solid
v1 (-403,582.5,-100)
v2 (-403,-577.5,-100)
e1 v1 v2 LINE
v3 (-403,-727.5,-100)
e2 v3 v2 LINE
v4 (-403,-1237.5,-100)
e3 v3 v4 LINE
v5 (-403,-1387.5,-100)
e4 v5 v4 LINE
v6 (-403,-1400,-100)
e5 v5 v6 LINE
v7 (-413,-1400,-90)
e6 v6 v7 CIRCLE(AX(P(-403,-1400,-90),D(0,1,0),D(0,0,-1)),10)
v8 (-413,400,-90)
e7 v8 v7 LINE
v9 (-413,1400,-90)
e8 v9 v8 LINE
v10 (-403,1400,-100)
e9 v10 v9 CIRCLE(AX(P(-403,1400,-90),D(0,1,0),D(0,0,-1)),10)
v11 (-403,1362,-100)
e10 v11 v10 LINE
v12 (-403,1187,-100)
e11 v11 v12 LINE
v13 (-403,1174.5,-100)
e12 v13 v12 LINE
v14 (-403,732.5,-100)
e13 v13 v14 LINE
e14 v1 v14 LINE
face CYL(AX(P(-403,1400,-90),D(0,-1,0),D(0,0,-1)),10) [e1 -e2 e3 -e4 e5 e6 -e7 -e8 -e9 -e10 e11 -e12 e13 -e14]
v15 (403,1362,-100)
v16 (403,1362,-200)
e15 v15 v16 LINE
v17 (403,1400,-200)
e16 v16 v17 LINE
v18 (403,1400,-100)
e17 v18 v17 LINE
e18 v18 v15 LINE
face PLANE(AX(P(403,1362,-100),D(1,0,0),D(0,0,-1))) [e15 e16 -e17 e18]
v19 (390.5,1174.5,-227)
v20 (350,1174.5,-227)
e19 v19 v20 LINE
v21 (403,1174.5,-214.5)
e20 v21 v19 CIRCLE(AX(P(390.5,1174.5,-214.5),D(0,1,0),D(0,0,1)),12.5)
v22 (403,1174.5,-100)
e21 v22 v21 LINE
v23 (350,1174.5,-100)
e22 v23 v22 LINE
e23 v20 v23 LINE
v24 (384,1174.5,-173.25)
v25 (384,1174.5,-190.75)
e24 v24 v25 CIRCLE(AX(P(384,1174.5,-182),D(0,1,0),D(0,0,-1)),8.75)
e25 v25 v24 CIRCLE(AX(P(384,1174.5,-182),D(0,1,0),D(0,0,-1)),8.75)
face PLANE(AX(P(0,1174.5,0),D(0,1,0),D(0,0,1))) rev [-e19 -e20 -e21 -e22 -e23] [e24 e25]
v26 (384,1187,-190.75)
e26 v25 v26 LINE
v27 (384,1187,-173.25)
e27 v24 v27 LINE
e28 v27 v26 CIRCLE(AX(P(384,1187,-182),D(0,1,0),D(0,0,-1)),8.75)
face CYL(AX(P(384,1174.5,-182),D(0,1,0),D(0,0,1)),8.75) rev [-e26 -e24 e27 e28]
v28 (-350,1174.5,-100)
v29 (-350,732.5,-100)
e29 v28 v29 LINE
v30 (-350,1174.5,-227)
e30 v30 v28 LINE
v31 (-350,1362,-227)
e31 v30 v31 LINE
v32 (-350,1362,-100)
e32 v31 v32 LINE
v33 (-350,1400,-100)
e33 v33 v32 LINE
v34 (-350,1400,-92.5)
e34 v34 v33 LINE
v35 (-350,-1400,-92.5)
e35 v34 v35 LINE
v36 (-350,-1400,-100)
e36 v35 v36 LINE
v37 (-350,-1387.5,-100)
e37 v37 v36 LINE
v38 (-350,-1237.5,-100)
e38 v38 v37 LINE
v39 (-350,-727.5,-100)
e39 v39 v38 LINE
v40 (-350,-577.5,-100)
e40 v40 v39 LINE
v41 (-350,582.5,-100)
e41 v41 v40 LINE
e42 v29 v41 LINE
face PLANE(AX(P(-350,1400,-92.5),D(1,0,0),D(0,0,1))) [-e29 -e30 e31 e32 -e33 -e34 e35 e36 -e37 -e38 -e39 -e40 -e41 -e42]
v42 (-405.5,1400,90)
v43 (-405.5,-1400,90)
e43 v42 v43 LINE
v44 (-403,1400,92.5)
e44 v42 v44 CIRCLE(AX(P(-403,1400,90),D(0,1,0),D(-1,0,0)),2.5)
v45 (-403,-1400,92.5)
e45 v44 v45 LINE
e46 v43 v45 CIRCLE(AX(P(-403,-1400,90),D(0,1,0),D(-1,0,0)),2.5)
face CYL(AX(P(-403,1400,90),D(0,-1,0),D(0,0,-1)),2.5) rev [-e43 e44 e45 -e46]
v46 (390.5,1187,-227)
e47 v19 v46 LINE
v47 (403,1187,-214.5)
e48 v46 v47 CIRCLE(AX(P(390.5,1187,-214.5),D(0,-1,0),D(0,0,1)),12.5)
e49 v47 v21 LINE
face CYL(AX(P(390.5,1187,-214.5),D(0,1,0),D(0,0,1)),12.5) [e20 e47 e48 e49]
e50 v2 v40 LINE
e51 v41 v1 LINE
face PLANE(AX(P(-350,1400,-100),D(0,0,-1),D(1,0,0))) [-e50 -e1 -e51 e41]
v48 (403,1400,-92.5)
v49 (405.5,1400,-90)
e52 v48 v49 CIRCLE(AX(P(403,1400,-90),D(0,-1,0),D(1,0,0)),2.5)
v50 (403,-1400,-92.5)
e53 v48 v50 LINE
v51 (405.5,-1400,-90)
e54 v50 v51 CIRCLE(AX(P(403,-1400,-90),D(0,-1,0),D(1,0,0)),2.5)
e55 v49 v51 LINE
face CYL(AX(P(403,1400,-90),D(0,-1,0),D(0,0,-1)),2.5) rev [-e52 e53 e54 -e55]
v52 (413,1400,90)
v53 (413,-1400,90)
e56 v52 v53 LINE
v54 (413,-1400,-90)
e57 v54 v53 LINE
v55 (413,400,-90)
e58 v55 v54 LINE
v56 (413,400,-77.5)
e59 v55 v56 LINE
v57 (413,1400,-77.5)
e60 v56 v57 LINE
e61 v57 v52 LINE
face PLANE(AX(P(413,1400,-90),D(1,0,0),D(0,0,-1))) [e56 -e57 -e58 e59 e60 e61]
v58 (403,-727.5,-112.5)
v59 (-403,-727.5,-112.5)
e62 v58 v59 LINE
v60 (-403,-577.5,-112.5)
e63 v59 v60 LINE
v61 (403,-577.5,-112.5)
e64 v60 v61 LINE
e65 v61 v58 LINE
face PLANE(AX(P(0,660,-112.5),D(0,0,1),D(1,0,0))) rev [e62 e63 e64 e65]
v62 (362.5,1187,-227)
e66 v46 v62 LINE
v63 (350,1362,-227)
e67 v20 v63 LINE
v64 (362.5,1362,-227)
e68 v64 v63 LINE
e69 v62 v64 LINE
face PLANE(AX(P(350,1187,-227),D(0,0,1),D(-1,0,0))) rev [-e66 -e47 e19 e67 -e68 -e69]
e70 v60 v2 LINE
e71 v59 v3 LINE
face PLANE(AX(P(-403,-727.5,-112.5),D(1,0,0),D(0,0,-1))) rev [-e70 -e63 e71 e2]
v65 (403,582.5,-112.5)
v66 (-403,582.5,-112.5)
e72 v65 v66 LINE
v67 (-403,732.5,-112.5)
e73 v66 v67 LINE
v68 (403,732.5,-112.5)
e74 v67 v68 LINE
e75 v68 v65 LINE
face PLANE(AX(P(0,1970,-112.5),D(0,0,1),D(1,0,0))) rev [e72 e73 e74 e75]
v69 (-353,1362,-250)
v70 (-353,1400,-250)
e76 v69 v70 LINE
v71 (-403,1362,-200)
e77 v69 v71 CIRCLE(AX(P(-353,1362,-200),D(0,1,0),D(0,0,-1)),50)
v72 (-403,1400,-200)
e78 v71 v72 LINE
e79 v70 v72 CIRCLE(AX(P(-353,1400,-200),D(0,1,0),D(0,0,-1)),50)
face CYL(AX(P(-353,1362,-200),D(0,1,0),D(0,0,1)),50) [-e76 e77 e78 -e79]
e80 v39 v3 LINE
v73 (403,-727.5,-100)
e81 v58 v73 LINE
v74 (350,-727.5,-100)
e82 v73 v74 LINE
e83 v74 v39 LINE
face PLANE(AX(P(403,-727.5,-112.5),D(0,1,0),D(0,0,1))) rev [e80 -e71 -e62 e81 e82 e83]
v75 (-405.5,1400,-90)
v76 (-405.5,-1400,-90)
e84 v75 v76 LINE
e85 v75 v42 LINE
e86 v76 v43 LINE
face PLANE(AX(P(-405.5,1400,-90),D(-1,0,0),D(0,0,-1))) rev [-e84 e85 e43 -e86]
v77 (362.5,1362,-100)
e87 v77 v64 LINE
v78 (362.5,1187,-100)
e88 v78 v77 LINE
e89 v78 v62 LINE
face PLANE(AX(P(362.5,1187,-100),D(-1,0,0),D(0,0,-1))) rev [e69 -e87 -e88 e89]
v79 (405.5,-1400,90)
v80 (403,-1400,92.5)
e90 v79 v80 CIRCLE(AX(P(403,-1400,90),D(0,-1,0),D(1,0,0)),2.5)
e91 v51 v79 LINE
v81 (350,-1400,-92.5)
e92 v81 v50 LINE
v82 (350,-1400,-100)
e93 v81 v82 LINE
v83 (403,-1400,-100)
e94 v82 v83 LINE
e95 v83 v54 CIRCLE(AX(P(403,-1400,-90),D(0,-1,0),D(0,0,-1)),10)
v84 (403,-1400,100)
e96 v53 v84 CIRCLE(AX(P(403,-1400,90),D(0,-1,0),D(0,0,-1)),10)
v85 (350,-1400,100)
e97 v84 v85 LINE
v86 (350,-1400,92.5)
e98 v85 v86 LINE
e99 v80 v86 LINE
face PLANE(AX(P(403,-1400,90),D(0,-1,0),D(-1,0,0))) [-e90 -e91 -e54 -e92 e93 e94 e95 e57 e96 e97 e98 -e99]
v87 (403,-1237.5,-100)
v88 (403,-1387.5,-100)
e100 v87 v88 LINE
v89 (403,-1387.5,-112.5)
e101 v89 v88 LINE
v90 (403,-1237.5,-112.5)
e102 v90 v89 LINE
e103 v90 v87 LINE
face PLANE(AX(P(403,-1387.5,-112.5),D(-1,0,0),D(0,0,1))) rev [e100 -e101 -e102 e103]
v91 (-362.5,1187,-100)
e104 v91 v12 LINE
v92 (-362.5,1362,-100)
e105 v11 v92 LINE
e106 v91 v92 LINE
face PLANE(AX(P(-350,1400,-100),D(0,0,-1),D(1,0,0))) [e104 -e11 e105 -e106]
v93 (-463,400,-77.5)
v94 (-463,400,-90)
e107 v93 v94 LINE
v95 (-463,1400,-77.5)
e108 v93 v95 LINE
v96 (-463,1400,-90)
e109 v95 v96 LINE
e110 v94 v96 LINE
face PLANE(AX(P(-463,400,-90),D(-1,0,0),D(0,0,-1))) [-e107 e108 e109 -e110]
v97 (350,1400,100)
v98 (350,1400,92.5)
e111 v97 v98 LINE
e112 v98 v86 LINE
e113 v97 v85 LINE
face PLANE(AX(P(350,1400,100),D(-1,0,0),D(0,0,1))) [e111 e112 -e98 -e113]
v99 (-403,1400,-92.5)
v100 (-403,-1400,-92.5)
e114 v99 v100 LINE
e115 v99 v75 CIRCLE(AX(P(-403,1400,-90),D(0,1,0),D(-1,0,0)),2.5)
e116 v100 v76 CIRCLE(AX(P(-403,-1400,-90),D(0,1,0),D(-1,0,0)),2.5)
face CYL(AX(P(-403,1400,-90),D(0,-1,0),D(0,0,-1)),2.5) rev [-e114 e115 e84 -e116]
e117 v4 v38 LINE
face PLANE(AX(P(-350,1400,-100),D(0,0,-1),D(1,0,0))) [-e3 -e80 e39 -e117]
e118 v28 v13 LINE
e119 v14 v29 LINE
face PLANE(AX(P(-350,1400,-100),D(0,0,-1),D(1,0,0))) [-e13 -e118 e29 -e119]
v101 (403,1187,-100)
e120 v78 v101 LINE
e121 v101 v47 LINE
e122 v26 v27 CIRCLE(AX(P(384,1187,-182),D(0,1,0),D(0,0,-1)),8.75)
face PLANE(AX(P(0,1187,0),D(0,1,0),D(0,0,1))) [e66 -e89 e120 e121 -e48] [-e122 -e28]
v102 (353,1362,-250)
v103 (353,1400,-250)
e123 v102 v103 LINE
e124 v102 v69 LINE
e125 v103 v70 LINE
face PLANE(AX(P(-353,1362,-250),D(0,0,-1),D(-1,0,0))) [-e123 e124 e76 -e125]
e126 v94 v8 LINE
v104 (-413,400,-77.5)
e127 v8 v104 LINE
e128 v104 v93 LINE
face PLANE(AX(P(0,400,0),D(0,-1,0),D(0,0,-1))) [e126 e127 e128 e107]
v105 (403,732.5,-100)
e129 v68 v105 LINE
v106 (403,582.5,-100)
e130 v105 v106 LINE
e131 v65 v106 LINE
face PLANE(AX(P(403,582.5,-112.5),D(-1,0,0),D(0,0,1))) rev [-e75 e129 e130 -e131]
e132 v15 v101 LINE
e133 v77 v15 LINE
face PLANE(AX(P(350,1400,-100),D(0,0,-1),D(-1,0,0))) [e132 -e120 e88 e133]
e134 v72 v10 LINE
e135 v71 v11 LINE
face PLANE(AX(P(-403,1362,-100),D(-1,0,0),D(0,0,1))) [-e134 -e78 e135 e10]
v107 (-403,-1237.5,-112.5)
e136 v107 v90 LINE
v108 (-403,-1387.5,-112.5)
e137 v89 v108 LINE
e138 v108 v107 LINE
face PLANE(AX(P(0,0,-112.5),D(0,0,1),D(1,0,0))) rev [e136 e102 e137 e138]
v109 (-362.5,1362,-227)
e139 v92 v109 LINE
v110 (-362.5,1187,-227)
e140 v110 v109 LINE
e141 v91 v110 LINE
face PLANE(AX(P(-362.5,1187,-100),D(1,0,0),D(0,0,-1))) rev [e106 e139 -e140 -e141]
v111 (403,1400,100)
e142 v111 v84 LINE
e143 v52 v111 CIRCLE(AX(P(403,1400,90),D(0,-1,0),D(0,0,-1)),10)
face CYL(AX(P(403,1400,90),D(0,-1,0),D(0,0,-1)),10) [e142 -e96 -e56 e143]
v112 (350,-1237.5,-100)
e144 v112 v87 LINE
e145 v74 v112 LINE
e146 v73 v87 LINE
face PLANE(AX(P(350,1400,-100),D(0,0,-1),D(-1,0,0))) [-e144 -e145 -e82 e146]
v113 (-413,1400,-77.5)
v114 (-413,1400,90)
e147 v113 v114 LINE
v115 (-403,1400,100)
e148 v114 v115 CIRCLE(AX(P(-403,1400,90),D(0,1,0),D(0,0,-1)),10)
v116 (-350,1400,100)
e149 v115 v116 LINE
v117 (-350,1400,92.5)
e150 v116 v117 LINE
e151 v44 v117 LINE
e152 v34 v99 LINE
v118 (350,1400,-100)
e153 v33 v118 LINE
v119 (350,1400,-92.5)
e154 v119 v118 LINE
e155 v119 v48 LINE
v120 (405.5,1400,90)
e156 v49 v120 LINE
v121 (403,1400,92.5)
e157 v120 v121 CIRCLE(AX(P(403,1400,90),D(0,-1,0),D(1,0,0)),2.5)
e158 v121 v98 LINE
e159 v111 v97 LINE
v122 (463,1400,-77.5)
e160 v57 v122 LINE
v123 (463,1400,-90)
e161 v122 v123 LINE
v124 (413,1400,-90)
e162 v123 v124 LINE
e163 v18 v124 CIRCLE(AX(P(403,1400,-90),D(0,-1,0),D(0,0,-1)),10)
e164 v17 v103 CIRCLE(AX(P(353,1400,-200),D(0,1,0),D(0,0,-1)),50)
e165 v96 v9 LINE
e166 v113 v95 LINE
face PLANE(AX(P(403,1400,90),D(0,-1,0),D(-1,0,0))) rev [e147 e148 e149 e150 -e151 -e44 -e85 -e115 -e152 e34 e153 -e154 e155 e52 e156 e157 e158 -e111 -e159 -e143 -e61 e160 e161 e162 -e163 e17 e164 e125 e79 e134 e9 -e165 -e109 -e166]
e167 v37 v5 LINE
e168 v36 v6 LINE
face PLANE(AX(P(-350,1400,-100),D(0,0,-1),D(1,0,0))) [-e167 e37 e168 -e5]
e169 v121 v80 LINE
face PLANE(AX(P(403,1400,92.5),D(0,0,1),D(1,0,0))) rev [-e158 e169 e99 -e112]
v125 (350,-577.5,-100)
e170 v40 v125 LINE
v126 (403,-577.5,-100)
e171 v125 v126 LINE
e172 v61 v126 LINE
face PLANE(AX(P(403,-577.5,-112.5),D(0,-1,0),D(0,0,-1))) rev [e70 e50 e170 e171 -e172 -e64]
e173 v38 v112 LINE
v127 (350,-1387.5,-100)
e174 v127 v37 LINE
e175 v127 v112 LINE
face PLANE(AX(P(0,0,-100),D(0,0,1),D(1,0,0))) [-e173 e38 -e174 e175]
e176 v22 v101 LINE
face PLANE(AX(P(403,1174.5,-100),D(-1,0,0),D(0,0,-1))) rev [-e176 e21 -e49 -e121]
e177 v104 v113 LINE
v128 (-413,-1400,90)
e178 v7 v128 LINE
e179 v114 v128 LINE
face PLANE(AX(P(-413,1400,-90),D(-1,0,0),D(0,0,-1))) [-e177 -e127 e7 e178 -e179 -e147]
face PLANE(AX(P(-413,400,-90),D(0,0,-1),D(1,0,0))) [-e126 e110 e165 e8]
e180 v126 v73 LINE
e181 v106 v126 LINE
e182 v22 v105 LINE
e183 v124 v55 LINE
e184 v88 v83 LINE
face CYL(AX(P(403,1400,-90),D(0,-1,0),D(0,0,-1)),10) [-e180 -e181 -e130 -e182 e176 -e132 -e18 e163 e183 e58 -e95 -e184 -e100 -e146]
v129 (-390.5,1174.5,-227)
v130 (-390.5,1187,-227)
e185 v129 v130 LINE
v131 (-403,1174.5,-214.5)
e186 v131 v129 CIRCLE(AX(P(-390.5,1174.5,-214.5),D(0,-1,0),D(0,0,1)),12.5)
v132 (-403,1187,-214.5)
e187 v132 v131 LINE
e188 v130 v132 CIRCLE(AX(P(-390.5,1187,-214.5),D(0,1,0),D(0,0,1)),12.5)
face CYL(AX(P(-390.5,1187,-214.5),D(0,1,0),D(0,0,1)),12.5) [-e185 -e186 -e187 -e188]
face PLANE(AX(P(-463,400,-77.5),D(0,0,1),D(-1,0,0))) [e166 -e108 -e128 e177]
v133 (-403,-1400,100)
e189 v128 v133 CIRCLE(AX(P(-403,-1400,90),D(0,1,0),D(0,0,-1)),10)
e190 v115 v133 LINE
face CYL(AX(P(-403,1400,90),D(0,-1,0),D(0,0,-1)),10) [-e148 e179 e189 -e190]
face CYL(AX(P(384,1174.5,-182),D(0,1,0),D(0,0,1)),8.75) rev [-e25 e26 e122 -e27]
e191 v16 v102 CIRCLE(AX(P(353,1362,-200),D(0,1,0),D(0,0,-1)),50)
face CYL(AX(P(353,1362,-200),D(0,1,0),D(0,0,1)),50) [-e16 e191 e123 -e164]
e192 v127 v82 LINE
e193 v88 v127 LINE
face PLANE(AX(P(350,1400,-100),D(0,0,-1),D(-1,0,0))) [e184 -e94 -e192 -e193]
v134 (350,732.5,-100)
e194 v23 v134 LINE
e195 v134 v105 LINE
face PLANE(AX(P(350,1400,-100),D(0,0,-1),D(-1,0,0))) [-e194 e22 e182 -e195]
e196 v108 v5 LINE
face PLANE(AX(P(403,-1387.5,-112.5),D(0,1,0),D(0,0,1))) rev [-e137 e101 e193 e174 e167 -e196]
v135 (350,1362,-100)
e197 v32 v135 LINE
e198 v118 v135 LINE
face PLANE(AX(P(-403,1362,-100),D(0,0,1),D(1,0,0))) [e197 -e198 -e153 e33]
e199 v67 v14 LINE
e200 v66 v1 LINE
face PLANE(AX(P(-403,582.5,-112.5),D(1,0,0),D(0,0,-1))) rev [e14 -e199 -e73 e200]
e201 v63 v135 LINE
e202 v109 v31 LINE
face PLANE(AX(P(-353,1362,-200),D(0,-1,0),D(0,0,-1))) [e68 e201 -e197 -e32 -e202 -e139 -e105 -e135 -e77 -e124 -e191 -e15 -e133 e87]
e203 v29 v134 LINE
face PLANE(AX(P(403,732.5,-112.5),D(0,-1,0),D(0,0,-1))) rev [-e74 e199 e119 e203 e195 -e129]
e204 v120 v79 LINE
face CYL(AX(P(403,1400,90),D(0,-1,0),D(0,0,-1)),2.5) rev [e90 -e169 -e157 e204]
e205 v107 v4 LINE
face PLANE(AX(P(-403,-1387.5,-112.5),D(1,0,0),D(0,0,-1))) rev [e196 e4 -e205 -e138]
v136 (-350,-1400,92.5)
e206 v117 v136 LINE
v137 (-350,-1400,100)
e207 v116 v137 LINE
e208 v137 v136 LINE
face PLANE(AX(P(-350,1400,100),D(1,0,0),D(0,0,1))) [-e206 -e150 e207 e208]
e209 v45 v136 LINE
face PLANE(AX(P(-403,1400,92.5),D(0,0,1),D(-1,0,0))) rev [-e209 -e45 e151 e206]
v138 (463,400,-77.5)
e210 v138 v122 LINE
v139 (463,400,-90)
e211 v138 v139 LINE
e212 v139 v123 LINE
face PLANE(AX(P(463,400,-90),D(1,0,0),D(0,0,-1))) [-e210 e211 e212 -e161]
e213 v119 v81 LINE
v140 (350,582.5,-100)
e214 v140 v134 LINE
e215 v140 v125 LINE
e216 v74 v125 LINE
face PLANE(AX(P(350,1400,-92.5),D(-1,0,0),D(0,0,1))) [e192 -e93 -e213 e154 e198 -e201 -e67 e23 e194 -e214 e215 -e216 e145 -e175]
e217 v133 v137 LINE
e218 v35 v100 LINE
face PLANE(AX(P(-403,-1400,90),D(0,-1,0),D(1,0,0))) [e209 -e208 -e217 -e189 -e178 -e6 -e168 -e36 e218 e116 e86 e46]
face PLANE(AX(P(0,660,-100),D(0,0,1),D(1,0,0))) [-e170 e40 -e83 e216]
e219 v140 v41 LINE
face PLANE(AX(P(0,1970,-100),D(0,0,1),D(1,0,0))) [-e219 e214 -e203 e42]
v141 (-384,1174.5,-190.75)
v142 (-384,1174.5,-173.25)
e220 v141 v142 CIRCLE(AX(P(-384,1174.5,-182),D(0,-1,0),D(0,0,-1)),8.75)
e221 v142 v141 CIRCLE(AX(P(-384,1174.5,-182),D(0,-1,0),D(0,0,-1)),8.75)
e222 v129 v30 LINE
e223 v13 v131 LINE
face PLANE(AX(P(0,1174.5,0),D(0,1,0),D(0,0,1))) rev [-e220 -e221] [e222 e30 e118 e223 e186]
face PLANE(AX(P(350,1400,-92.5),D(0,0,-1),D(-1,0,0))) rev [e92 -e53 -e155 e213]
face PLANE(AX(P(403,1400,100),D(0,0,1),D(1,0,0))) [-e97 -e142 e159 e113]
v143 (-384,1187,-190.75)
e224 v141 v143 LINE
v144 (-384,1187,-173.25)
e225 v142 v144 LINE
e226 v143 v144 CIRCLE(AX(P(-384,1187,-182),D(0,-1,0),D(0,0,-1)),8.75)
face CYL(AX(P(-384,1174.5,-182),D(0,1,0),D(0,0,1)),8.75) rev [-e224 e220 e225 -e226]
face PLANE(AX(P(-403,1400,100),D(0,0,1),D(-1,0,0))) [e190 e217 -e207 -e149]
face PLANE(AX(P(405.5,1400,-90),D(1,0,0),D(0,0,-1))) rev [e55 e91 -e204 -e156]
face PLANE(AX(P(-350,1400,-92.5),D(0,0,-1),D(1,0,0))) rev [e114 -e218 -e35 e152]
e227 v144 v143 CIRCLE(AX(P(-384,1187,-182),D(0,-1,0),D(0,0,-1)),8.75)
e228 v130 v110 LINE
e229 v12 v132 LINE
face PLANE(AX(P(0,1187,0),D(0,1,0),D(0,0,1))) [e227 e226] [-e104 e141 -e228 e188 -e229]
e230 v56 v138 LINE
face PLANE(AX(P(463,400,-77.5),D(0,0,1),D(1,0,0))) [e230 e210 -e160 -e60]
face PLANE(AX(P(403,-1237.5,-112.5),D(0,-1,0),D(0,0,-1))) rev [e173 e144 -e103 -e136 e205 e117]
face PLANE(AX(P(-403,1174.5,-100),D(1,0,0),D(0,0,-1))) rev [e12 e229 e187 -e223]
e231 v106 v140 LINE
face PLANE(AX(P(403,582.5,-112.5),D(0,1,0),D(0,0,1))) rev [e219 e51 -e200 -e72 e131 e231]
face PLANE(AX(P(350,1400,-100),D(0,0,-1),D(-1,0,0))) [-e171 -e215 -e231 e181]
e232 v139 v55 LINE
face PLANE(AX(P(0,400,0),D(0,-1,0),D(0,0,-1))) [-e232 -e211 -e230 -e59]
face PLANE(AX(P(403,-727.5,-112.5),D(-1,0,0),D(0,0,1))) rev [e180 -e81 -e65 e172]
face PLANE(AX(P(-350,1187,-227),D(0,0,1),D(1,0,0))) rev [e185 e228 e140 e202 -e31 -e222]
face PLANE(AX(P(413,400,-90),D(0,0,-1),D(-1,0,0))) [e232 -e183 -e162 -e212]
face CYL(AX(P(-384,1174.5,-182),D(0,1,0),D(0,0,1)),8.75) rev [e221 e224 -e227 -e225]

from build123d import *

# Parameters (mm, degrees)
SIDE_CHANNEL_RAIL_L2800_DEPTH = 1400
TOP_CAP_SKETCH_W              = 50
TOP_CAP_SKETCH_H              = 12.5
TOP_CAP_PLATE_DEPTH           = 1000
SIDE_BRACKET_DEPTH            = 38
CROSS_BAR_SKETCH_W            = 806
CROSS_BAR_SKETCH_H            = 150
CROSS_BAR_DEPTH               = 12.5
CROSS_BAR_PATTERN_660_COUNT   = 2
CROSS_BAR_PATTERN_660_PITCH   = 660
CROSS_BAR_PATTERN_1970_COUNT  = 2
CROSS_BAR_PATTERN_1970_PITCH  = 1970
HANGER_PLATE_SKETCH_W         = 12.5
HANGER_PLATE_SKETCH_H         = 127
HANGER_PLATE_DEPTH            = 175
HANGER_TAB_SKETCH_W           = 53
HANGER_TAB_SKETCH_H           = 127
HANGER_TAB_SKETCH_R           = 8.75
HANGER_TAB_DEPTH              = 12.5
HANGER_TAB_FILLET_R12_5_R     = 12.5


with BuildPart() as part:
    # Side Channel Profile Sketch → Side Channel Rail L2800 (new, symmetric)
    with BuildSketch(Plane(origin=(0, 0, 0), x_dir=(1, 0, 0), z_dir=(0, 1, 0))):
        with BuildLine():
            Line((350, 100), (403, 100))
            ThreePointArc((403, 100), (410.071067812, 97.071067812), (413, 90))
            Line((413, 90), (413, -90))
            ThreePointArc((413, -90), (410.071067812, -97.071067812), (403, -100))
            Line((403, -100), (350, -100))
            Line((350, -100), (350, -92.5))
            Line((350, -92.5), (403, -92.5))
            ThreePointArc((403, -92.5), (404.767766953, -91.767766953), (405.5, -90))
            Line((405.5, -90), (405.5, 90))
            ThreePointArc((405.5, 90), (404.767766953, 91.767766953), (403, 92.5))
            Line((403, 92.5), (350, 92.5))
            Line((350, 92.5), (350, 100))
        make_face()
    extrude(amount=SIDE_CHANNEL_RAIL_L2800_DEPTH, both=True)

    # Top Cap Sketch → Top Cap Plate (add)
    with BuildSketch(Plane(origin=(0, 1400, 0), x_dir=(1, 0, 0), z_dir=(0, 1, 0))):
        with Locations((438, 83.75)):
            Rectangle(TOP_CAP_SKETCH_W, TOP_CAP_SKETCH_H)
    extrude(amount=-TOP_CAP_PLATE_DEPTH)


with BuildPart() as body_2:
    # Side Rail Mirror: mirrored copy
    add(part.part.mirror(Plane(origin=(0, 0, 0), x_dir=(0, 0, 1), z_dir=(1, 0, 0))))


with BuildPart() as part_1:
    add(part.part)

    add(body_2.part)  # Side Bracket merges body 2
    # Bracket Sketch → Side Bracket (add)
    with BuildSketch(Plane(origin=(0, 1400, 0), x_dir=(1, 0, 0), z_dir=(0, 1, 0))):
        with BuildLine():
            Line((-403, 100), (403, 100))
            Line((403, 100), (403, 200))
            ThreePointArc((403, 200), (388.355339059, 235.355339059), (353, 250))
            Line((353, 250), (-353, 250))
            ThreePointArc((-353, 250), (-388.355339059, 235.355339059), (-403, 200))
            Line((-403, 200), (-403, 100))
        make_face()
    extrude(amount=-SIDE_BRACKET_DEPTH)

    # Cross Bar Sketch → Cross Bar (add)
    with BuildSketch(Plane(origin=(0, 0, -100), x_dir=(-1, 0, 0), z_dir=(0, 0, -1))):
        with Locations((0, -1312.5)):
            Rectangle(CROSS_BAR_SKETCH_W, CROSS_BAR_SKETCH_H)
    cross_bar = extrude(amount=CROSS_BAR_DEPTH)

    # Cross Bar Pattern 660: Cross Bar ×2
    with Locations(*[(0, i * CROSS_BAR_PATTERN_660_PITCH, 0) for i in range(1, CROSS_BAR_PATTERN_660_COUNT)]):
        add(cross_bar)

    # Cross Bar Pattern 1970: Cross Bar ×2
    with Locations(*[(0, i * CROSS_BAR_PATTERN_1970_PITCH, 0) for i in range(1, CROSS_BAR_PATTERN_1970_COUNT)]):
        add(cross_bar)

    # Hanger Plate Sketch → Hanger Plate (add)
    with BuildSketch(Plane.XZ.offset(-1362)):
        with Locations((-356.25, -163.5)):
            Rectangle(HANGER_PLATE_SKETCH_W, HANGER_PLATE_SKETCH_H)
    extrude(amount=HANGER_PLATE_DEPTH)

    # Hanger Tab Sketch → Hanger Tab (add)
    with BuildSketch(Plane.XZ.offset(-1187)):
        with Locations((-376.5, -163.5)):
            Rectangle(HANGER_TAB_SKETCH_W, HANGER_TAB_SKETCH_H)
        with Locations(Location((-384, -182, 0), (0, 0, 270))):
            Circle(HANGER_TAB_SKETCH_R, mode=Mode.SUBTRACT)
    extrude(amount=HANGER_TAB_DEPTH)

    # Hanger Tab Fillet R12.5
    hanger_tab_fillet_r12_5_edges = [part_1.edges().sort_by_distance(p)[0] for p in [
        (-403, 1180.75, -227),
    ]]
    fillet(hanger_tab_fillet_r12_5_edges, radius=HANGER_TAB_FILLET_R12_5_R)

    # Side Bracket Mirror: part across plane


with BuildPart() as part_2:
    add(part_1.part)
    add(part_1.part.mirror(Plane(origin=(0, 0, 0), x_dir=(0, 0, 1), z_dir=(1, 0, 0))))


solid = part_2.part
